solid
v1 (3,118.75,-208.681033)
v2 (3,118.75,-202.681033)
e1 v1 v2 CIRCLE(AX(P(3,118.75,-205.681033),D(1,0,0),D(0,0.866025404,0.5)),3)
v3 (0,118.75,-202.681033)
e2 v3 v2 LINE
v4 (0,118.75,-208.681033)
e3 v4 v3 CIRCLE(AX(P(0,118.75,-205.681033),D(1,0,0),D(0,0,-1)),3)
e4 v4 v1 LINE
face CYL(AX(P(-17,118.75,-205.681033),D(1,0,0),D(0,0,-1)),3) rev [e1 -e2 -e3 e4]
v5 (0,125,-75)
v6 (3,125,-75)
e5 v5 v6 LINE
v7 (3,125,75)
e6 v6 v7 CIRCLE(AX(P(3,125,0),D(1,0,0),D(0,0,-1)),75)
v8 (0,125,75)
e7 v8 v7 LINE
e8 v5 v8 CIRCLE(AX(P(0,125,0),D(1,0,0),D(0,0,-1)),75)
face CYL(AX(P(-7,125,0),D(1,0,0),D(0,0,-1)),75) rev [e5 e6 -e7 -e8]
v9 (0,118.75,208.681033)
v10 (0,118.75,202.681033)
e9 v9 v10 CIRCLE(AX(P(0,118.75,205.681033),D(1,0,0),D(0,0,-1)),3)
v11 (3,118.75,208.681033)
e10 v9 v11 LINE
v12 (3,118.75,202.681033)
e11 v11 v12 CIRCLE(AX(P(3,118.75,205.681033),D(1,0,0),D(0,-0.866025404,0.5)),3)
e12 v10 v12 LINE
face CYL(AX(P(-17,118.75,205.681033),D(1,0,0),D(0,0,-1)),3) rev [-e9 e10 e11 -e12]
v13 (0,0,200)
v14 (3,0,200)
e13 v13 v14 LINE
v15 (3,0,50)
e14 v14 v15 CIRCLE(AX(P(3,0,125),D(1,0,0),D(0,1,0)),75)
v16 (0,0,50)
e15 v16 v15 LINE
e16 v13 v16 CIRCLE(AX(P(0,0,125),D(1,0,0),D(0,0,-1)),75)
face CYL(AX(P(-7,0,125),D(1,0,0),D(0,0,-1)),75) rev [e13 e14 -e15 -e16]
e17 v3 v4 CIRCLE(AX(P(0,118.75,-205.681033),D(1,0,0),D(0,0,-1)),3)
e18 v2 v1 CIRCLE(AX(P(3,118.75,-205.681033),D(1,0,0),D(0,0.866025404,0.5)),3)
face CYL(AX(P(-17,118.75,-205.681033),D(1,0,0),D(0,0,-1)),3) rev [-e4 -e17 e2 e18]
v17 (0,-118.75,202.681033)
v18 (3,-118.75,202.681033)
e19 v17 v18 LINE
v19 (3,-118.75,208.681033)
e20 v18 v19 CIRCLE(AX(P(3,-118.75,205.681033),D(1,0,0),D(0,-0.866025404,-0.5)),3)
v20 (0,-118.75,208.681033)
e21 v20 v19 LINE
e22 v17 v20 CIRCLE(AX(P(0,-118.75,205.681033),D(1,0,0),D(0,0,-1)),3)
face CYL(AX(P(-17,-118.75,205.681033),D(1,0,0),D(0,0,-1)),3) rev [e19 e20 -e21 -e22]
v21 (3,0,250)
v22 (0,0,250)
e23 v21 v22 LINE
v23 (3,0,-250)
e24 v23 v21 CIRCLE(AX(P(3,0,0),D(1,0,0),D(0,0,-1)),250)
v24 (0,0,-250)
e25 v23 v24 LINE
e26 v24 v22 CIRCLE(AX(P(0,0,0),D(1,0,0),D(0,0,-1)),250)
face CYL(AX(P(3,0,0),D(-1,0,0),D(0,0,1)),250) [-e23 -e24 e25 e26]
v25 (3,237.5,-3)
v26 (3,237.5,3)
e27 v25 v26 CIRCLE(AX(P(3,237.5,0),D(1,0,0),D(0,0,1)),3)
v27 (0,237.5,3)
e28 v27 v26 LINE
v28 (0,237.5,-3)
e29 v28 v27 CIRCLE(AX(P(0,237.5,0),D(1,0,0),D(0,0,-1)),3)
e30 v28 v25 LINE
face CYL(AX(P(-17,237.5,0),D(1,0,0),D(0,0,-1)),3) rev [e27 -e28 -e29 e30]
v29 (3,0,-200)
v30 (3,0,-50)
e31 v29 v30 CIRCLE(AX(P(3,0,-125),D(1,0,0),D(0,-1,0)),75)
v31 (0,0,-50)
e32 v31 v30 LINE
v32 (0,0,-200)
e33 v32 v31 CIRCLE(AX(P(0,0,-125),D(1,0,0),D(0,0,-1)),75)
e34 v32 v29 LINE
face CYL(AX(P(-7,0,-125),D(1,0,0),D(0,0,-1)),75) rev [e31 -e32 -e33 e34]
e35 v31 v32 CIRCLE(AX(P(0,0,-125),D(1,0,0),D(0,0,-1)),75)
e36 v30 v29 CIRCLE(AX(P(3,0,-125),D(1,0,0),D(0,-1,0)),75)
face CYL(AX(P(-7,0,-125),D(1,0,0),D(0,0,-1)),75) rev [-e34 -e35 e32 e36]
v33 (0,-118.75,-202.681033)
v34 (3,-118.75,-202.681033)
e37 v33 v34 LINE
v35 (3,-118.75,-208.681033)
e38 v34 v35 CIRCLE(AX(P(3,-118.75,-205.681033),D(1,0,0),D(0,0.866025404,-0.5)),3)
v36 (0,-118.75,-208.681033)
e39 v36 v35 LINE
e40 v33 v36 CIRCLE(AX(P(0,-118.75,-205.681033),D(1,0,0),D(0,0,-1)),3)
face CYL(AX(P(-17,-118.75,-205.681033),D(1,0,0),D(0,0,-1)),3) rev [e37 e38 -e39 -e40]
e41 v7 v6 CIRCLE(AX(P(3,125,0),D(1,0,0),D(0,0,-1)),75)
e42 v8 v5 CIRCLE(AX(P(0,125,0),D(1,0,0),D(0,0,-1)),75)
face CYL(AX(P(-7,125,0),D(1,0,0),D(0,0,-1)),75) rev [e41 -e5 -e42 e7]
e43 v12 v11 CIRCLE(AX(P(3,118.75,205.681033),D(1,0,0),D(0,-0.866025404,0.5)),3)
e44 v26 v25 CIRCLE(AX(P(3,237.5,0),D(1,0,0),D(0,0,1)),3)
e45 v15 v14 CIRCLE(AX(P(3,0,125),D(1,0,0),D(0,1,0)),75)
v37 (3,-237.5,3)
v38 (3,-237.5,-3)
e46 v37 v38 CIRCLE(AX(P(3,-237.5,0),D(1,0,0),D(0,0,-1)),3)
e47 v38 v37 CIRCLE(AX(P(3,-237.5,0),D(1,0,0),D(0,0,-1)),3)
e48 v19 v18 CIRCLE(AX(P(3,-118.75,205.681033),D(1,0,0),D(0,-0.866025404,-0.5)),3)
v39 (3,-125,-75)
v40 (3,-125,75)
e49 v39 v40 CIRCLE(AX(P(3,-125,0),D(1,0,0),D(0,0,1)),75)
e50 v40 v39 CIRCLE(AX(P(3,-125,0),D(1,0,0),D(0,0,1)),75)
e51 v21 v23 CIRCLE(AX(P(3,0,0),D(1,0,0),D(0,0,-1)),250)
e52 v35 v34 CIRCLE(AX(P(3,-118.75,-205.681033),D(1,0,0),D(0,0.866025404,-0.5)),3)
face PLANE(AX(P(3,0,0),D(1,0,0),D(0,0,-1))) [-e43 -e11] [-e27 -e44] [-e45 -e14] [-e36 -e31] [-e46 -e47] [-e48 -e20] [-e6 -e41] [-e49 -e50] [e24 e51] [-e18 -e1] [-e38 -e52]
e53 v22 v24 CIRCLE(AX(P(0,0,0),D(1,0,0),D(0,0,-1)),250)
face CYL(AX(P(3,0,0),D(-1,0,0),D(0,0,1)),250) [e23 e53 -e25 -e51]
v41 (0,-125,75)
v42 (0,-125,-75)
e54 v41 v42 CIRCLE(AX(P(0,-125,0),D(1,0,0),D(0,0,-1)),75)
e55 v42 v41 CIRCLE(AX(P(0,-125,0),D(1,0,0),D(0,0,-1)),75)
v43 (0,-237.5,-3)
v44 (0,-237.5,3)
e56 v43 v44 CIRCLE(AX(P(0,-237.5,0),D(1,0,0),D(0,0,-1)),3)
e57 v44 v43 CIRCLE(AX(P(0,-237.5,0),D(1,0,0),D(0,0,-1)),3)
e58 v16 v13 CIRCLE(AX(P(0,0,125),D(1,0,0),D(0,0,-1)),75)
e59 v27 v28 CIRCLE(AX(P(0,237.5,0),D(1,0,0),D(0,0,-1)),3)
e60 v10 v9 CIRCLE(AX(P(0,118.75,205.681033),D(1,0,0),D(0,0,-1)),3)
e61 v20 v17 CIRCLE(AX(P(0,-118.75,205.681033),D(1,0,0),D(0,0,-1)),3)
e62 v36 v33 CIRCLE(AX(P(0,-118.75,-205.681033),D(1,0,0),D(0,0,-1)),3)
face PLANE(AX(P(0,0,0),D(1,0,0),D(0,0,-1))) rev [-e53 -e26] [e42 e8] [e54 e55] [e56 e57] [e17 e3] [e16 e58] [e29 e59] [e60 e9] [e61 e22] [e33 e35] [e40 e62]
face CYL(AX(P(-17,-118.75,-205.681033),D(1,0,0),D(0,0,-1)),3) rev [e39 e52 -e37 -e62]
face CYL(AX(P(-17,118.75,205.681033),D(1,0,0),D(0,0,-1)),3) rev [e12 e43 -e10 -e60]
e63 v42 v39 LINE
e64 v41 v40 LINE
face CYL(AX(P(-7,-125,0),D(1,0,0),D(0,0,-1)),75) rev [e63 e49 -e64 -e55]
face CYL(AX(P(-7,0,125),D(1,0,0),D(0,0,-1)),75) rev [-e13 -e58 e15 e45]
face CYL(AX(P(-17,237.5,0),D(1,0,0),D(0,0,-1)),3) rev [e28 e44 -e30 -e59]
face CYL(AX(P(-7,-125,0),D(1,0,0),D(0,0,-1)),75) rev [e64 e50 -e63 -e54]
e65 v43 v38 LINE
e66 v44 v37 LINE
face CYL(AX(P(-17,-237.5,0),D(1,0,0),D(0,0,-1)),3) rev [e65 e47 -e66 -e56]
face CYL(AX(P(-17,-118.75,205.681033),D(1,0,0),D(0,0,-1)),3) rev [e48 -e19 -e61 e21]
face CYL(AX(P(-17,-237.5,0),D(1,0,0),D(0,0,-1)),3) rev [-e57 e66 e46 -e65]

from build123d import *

# Parameters (mm, degrees)
SKETCH1_R           = 250
BOSS_EXTRUDE1_DEPTH = 3
SKETCH2_R           = 75
CUT_EXTRUDE1_DEPTH  = 10
CIRPATTERN1_COUNT   = 4
SKETCH3_R           = 3
CUT_EXTRUDE2_DEPTH  = 20
CIRPATTERN2_COUNT   = 6


with BuildPart() as part:
    # Sketch1 → Boss-Extrude1 (new body)
    with BuildSketch(Plane(origin=(0, 0, 0), x_dir=(0, 0, -1), z_dir=(1, 0, 0))):
        Circle(SKETCH1_R)
    extrude(amount=BOSS_EXTRUDE1_DEPTH)

    # Sketch2 → Cut-Extrude1 (cut)
    with BuildSketch(Plane(origin=(3, 0, 0), x_dir=(0, 0, -1), z_dir=(1, 0, 0))):
        with Locations((0, 125)):
            Circle(SKETCH2_R)
    cut_extrude1 = extrude(amount=-CUT_EXTRUDE1_DEPTH, mode=Mode.SUBTRACT)

    # CirPattern1: Cut-Extrude1 ×4 about axis
    cirpattern1_axis = Axis((0, 0, 0), (1, 0, 0))
    for i in range(1, CIRPATTERN1_COUNT):
        add(cut_extrude1.rotate(cirpattern1_axis, i * 360 / CIRPATTERN1_COUNT), mode=Mode.SUBTRACT)

    # Sketch3 → Cut-Extrude2 (cut)
    with BuildSketch(Plane(origin=(3, 0, 0), x_dir=(0, 0, -1), z_dir=(1, 0, 0))):
        with Locations((0, -237.5)):
            Circle(SKETCH3_R)
    cut_extrude2 = extrude(amount=-CUT_EXTRUDE2_DEPTH, mode=Mode.SUBTRACT)

    # CirPattern2: Cut-Extrude2 ×6 about axis
    cirpattern2_axis = Axis((0, 0, 0), (1, 0, 0))
    for i in range(1, CIRPATTERN2_COUNT):
        add(cut_extrude2.rotate(cirpattern2_axis, i * 360 / CIRPATTERN2_COUNT), mode=Mode.SUBTRACT)


solid = part.part
